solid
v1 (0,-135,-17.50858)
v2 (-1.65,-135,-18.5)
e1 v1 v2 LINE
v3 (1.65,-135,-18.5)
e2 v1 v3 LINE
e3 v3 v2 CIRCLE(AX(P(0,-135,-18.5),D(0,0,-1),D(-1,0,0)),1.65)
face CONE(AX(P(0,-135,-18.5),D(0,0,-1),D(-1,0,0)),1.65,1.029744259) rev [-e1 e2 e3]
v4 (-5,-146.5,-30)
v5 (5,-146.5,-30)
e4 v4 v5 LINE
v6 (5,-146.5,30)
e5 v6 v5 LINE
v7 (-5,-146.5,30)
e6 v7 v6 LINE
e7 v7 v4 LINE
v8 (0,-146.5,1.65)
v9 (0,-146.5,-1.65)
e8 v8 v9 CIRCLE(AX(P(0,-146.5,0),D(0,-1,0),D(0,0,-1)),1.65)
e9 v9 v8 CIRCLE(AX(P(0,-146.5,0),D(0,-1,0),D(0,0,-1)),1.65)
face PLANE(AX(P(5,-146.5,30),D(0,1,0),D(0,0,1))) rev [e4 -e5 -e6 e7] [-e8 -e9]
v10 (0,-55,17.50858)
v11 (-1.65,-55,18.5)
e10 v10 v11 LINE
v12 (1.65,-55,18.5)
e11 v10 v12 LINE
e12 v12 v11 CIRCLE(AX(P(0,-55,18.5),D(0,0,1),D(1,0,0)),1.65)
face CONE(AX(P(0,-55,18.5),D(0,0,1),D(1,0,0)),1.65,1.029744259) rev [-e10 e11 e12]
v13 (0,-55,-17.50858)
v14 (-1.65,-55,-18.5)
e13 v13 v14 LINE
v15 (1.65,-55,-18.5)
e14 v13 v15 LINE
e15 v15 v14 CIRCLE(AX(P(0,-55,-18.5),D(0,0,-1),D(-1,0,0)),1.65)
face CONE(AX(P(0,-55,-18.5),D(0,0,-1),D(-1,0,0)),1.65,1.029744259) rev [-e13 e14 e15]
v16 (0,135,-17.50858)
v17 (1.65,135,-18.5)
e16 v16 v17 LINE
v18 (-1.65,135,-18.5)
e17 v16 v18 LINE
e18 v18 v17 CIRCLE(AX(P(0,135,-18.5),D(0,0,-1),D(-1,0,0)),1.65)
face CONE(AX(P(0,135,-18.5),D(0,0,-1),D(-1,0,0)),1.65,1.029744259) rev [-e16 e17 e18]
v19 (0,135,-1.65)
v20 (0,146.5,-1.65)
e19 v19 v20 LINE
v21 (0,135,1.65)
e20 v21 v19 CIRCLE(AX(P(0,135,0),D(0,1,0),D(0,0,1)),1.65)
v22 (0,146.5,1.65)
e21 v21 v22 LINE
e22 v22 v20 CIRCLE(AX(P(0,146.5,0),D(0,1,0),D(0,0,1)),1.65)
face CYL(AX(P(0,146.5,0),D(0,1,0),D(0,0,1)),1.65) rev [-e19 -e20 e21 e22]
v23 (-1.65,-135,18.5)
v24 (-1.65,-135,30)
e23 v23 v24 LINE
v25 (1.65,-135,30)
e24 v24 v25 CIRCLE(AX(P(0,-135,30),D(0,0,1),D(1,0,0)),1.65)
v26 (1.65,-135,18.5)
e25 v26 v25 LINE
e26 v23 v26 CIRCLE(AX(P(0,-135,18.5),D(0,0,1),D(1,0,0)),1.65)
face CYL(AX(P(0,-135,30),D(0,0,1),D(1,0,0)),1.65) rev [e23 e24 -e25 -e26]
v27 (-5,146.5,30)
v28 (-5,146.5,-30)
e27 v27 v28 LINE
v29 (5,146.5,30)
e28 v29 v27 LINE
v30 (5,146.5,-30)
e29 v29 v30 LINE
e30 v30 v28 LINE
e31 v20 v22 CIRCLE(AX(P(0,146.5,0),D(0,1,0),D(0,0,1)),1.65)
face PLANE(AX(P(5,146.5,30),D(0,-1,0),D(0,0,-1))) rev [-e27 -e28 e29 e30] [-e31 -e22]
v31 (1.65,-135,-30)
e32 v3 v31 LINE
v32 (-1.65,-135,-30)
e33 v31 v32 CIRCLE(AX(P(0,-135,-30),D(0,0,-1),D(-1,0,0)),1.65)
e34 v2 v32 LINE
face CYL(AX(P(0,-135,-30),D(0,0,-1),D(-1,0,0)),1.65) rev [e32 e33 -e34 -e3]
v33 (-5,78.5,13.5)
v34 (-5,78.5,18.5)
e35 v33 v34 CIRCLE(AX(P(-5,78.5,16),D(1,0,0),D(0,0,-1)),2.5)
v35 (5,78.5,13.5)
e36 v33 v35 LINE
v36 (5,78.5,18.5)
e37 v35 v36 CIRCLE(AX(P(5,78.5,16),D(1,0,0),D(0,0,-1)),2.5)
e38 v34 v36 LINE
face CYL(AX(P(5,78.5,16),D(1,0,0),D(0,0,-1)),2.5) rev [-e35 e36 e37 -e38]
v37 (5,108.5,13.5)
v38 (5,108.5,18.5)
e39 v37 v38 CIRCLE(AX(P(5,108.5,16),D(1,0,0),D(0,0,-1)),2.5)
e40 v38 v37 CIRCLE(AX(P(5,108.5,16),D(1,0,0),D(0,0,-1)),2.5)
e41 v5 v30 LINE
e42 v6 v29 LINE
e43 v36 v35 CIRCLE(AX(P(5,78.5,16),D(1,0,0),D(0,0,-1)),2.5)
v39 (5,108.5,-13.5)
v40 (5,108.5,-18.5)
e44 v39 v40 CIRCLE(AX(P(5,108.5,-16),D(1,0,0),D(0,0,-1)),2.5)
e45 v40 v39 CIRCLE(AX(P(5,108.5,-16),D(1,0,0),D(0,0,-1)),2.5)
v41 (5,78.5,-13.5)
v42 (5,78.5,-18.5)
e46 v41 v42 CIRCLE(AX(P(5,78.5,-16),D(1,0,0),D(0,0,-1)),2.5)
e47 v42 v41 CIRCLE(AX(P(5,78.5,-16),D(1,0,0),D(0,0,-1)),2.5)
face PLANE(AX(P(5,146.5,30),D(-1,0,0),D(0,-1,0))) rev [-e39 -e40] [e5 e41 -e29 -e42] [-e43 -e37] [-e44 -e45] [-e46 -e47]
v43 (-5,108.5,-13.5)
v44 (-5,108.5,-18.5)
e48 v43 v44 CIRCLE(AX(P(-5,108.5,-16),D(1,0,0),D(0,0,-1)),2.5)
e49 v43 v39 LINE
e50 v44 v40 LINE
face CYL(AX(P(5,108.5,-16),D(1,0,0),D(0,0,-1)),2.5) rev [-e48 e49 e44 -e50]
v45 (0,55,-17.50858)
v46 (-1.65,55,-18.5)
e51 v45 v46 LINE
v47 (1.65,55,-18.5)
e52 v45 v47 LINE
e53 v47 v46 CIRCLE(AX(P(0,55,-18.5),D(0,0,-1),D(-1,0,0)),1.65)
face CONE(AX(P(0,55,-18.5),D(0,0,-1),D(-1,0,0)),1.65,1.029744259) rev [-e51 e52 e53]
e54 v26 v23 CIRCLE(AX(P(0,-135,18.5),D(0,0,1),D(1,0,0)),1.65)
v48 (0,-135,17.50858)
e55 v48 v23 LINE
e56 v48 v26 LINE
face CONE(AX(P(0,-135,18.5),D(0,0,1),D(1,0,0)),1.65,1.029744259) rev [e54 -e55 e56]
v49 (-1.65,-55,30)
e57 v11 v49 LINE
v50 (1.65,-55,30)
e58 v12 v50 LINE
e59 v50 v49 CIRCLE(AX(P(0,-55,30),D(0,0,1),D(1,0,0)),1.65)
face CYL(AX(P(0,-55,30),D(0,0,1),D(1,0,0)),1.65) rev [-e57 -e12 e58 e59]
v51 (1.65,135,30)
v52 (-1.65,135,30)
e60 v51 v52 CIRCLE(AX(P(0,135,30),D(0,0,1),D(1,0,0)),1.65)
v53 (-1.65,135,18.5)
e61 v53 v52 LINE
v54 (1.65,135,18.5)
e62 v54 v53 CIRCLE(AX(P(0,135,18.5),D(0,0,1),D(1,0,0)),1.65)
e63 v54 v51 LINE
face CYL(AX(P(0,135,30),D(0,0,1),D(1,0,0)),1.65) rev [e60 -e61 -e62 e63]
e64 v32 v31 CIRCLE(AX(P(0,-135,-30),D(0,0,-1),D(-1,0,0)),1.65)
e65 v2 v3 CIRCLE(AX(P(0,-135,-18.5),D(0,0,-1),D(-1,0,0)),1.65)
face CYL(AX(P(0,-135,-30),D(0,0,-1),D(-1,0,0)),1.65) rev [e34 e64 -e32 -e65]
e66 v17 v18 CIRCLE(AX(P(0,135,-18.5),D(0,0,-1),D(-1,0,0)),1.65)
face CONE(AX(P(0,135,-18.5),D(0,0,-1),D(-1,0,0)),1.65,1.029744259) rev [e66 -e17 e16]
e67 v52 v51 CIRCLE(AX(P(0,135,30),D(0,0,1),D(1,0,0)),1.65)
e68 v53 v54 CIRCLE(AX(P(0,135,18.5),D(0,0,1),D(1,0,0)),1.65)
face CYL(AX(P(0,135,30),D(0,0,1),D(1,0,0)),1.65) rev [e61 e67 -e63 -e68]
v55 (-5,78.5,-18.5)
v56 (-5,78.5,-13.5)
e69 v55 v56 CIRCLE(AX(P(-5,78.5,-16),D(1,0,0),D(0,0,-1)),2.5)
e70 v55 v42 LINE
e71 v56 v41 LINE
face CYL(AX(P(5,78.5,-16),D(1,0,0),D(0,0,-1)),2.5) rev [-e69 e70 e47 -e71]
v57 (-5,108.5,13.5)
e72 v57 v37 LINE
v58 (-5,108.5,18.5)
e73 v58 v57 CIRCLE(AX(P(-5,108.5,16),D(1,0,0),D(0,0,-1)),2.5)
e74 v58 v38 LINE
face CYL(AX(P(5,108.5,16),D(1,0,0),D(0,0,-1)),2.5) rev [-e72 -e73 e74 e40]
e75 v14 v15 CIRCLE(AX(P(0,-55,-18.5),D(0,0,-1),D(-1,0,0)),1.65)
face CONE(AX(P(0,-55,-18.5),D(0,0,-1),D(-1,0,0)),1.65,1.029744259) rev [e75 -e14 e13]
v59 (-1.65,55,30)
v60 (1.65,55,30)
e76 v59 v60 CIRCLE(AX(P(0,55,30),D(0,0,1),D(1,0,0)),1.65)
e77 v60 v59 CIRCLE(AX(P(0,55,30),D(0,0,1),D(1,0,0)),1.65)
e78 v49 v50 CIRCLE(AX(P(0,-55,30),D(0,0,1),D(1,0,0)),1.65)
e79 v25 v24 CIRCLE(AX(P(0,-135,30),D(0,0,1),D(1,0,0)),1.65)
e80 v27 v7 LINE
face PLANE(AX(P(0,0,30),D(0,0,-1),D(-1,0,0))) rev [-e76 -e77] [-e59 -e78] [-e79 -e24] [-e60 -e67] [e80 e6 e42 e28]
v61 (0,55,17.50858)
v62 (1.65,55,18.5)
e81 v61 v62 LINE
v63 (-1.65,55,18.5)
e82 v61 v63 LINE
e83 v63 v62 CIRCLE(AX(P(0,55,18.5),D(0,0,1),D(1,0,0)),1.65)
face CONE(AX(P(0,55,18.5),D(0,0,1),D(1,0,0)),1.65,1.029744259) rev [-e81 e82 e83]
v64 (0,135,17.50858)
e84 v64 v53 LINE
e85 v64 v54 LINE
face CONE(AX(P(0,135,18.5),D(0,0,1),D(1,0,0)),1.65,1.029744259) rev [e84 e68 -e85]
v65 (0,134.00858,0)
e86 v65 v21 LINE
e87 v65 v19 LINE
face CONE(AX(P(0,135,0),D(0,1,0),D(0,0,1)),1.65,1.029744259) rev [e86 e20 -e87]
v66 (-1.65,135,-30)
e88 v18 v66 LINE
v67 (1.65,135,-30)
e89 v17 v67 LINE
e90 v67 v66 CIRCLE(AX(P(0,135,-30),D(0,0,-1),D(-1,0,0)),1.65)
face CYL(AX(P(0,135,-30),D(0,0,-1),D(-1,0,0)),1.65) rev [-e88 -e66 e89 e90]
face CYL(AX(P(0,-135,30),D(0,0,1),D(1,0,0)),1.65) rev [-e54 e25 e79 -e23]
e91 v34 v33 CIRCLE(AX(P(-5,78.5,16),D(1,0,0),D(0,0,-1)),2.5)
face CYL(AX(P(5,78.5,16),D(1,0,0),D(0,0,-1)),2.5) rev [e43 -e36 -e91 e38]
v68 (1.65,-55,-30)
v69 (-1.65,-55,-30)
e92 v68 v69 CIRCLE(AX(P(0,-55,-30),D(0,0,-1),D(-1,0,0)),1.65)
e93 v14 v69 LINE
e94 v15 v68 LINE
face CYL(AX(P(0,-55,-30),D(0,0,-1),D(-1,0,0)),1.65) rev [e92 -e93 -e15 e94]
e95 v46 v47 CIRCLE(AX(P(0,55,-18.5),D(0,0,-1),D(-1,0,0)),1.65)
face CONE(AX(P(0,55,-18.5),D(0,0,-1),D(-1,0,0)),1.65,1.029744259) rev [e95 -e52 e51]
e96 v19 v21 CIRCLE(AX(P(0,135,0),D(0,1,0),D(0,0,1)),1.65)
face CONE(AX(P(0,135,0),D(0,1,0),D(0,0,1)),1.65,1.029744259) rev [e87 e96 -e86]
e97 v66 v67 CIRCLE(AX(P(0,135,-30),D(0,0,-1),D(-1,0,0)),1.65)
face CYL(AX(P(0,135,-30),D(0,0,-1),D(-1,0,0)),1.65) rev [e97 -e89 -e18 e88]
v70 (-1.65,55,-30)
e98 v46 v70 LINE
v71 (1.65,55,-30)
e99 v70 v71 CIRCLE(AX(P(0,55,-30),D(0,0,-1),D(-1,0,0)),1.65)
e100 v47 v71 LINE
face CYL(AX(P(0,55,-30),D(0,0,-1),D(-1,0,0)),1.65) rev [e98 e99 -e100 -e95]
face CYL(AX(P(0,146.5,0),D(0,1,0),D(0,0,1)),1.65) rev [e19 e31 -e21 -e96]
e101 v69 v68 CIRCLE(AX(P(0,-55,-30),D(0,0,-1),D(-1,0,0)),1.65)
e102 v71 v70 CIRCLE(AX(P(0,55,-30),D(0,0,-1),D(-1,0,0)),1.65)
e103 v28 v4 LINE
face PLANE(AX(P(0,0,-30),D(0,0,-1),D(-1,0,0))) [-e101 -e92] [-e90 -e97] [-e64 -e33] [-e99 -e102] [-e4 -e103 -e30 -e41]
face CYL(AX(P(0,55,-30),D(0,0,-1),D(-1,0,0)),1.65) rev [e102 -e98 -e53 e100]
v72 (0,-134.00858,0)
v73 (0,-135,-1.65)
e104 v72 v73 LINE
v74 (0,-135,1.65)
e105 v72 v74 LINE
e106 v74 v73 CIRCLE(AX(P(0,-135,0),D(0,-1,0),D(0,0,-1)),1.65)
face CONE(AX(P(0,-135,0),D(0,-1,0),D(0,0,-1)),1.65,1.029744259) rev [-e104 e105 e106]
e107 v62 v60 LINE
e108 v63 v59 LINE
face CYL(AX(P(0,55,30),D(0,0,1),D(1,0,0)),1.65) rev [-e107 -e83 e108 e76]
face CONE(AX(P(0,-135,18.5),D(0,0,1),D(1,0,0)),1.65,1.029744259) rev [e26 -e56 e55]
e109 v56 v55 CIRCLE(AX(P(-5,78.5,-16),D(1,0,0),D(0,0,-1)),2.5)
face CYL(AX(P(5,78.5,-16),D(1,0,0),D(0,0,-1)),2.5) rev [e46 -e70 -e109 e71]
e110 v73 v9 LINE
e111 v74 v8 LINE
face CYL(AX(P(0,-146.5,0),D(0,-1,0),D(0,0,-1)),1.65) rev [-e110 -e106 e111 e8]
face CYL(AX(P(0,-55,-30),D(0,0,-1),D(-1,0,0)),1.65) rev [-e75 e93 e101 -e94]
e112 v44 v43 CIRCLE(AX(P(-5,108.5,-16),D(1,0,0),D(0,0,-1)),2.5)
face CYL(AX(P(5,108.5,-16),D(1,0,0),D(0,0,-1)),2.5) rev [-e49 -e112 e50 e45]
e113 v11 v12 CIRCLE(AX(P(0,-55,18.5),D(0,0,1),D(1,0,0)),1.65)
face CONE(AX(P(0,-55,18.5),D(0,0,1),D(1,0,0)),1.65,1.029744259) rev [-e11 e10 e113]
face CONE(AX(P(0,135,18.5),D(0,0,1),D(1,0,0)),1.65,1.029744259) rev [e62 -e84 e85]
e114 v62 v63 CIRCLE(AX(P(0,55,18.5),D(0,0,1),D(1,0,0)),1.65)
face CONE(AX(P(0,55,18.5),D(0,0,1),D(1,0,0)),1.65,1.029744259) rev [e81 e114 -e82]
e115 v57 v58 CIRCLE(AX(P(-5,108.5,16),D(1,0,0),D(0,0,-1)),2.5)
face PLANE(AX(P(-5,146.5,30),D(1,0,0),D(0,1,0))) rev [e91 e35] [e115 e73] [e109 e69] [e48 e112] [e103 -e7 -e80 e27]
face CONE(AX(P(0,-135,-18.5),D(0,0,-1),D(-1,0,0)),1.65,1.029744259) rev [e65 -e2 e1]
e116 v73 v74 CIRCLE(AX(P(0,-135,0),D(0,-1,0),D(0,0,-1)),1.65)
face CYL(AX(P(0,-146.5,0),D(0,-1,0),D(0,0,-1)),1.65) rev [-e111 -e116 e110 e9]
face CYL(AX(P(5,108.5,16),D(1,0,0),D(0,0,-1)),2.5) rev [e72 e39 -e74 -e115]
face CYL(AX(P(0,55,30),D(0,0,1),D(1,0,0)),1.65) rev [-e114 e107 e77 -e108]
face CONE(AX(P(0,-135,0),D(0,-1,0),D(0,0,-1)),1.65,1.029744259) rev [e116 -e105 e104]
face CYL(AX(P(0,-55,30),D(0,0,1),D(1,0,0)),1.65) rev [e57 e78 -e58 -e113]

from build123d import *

# Parameters (mm, degrees)
SKETCH1_W                  = 10
SKETCH1_H                  = 293
BOSS_EXTRUDE1_DEPTH        = 30
M4_TAPPED_HOLE1_AT_2_COUNT = 2
M4_TAPPED_HOLE1_AT_2_PITCH = 270
M4_TAPPED_HOLE1_AT_3_COUNT = 2
M4_TAPPED_HOLE1_AT_3_PITCH = 80
M4_TAPPED_HOLE1_AT_4_COUNT = 2
M4_TAPPED_HOLE1_AT_4_PITCH = 190
M6_TAPPED_HOLE1_D          = 5


with BuildPart() as part:
    # Sketch1 → Boss-Extrude1 (new, symmetric)
    with BuildSketch(Plane.XY):
        Rectangle(SKETCH1_W, SKETCH1_H)
    extrude(amount=BOSS_EXTRUDE1_DEPTH, both=True)

    # Sketch4 → M4 Tapped Hole1 (revolve, cut)
    with BuildSketch(Plane(origin=(0, 135, 30), x_dir=(0, -1, 0), z_dir=(1, 0, 0))):
        Polygon((0, 0), (0, 12.491420021), (1.65, 11.5), (1.65, 0), align=None)
    m4_tapped_hole1 = revolve(axis=Axis((0, 135, 36.35), (0, 0, -1)), mode=Mode.SUBTRACT)

    # M4 Tapped Hole1 at 2: M4 Tapped Hole1 ×2
    with Locations(*[(0, -i * M4_TAPPED_HOLE1_AT_2_PITCH, 0) for i in range(1, M4_TAPPED_HOLE1_AT_2_COUNT)]):
        add(m4_tapped_hole1, mode=Mode.SUBTRACT)

    # M4 Tapped Hole1 at 3: M4 Tapped Hole1 ×2
    with Locations(*[(0, -i * M4_TAPPED_HOLE1_AT_3_PITCH, 0) for i in range(1, M4_TAPPED_HOLE1_AT_3_COUNT)]):
        add(m4_tapped_hole1, mode=Mode.SUBTRACT)

    # M4 Tapped Hole1 at 4: M4 Tapped Hole1 ×2
    with Locations(*[(0, -i * M4_TAPPED_HOLE1_AT_4_PITCH, 0) for i in range(1, M4_TAPPED_HOLE1_AT_4_COUNT)]):
        add(m4_tapped_hole1, mode=Mode.SUBTRACT)

    # Sketch6 → M4 Tapped Hole2 (revolve, cut)
    with BuildSketch(Plane(origin=(0, -146.5, 0), x_dir=(0, 0, -1), z_dir=(1, 0, 0))):
        Polygon((0, 0), (0, 12.491420021), (1.65, 11.5), (1.65, 0), align=None)
    m4_tapped_hole2 = revolve(axis=Axis((0, -152.85, 0), (0, 1, 0)), mode=Mode.SUBTRACT)

    # Mirror1: M4 Tapped Hole2 across plane
    add(m4_tapped_hole2.mirror(Plane.ZX), mode=Mode.SUBTRACT)

    # M6 Tapped Hole1 (through all)
    with Locations(Plane(origin=(5, 0, 0), x_dir=(0, 0, -1), z_dir=(1, 0, 0))):
        with Locations((-16, 78.5), (16, 78.5), (16, 108.5), (-16, 108.5)):
            Hole(M6_TAPPED_HOLE1_D / 2)

    # Mirror2: M4 Tapped Hole1 across plane
    add(m4_tapped_hole1.mirror(Plane.XY), mode=Mode.SUBTRACT)

    # Mirror2 copy 1 sketch → Mirror2 copy 1 (revolve, cut)
    with BuildSketch(Plane(origin=(0, -135, -30), x_dir=(0, -1, 0), z_dir=(1, 0, 0))):
        Polygon((0, 0), (0, -12.491420021), (1.65, -11.5), (1.65, 0), align=None)
    revolve(axis=Axis((0, -135, -36.35), (0, 0, -1)), mode=Mode.SUBTRACT)

    # Mirror2 copy 2 sketch → Mirror2 copy 2 (revolve, cut)
    with BuildSketch(Plane(origin=(0, 55, -30), x_dir=(0, -1, 0), z_dir=(1, 0, 0))):
        Polygon((0, 0), (0, -12.491420021), (1.65, -11.5), (1.65, 0), align=None)
    revolve(axis=Axis((0, 55, -36.35), (0, 0, -1)), mode=Mode.SUBTRACT)

    # Mirror2 copy 3 sketch → Mirror2 copy 3 (revolve, cut)
    with BuildSketch(Plane(origin=(0, -55, -30), x_dir=(0, -1, 0), z_dir=(1, 0, 0))):
        Polygon((0, 0), (0, -12.491420021), (1.65, -11.5), (1.65, 0), align=None)
    revolve(axis=Axis((0, -55, -36.35), (0, 0, -1)), mode=Mode.SUBTRACT)


solid = part.part
